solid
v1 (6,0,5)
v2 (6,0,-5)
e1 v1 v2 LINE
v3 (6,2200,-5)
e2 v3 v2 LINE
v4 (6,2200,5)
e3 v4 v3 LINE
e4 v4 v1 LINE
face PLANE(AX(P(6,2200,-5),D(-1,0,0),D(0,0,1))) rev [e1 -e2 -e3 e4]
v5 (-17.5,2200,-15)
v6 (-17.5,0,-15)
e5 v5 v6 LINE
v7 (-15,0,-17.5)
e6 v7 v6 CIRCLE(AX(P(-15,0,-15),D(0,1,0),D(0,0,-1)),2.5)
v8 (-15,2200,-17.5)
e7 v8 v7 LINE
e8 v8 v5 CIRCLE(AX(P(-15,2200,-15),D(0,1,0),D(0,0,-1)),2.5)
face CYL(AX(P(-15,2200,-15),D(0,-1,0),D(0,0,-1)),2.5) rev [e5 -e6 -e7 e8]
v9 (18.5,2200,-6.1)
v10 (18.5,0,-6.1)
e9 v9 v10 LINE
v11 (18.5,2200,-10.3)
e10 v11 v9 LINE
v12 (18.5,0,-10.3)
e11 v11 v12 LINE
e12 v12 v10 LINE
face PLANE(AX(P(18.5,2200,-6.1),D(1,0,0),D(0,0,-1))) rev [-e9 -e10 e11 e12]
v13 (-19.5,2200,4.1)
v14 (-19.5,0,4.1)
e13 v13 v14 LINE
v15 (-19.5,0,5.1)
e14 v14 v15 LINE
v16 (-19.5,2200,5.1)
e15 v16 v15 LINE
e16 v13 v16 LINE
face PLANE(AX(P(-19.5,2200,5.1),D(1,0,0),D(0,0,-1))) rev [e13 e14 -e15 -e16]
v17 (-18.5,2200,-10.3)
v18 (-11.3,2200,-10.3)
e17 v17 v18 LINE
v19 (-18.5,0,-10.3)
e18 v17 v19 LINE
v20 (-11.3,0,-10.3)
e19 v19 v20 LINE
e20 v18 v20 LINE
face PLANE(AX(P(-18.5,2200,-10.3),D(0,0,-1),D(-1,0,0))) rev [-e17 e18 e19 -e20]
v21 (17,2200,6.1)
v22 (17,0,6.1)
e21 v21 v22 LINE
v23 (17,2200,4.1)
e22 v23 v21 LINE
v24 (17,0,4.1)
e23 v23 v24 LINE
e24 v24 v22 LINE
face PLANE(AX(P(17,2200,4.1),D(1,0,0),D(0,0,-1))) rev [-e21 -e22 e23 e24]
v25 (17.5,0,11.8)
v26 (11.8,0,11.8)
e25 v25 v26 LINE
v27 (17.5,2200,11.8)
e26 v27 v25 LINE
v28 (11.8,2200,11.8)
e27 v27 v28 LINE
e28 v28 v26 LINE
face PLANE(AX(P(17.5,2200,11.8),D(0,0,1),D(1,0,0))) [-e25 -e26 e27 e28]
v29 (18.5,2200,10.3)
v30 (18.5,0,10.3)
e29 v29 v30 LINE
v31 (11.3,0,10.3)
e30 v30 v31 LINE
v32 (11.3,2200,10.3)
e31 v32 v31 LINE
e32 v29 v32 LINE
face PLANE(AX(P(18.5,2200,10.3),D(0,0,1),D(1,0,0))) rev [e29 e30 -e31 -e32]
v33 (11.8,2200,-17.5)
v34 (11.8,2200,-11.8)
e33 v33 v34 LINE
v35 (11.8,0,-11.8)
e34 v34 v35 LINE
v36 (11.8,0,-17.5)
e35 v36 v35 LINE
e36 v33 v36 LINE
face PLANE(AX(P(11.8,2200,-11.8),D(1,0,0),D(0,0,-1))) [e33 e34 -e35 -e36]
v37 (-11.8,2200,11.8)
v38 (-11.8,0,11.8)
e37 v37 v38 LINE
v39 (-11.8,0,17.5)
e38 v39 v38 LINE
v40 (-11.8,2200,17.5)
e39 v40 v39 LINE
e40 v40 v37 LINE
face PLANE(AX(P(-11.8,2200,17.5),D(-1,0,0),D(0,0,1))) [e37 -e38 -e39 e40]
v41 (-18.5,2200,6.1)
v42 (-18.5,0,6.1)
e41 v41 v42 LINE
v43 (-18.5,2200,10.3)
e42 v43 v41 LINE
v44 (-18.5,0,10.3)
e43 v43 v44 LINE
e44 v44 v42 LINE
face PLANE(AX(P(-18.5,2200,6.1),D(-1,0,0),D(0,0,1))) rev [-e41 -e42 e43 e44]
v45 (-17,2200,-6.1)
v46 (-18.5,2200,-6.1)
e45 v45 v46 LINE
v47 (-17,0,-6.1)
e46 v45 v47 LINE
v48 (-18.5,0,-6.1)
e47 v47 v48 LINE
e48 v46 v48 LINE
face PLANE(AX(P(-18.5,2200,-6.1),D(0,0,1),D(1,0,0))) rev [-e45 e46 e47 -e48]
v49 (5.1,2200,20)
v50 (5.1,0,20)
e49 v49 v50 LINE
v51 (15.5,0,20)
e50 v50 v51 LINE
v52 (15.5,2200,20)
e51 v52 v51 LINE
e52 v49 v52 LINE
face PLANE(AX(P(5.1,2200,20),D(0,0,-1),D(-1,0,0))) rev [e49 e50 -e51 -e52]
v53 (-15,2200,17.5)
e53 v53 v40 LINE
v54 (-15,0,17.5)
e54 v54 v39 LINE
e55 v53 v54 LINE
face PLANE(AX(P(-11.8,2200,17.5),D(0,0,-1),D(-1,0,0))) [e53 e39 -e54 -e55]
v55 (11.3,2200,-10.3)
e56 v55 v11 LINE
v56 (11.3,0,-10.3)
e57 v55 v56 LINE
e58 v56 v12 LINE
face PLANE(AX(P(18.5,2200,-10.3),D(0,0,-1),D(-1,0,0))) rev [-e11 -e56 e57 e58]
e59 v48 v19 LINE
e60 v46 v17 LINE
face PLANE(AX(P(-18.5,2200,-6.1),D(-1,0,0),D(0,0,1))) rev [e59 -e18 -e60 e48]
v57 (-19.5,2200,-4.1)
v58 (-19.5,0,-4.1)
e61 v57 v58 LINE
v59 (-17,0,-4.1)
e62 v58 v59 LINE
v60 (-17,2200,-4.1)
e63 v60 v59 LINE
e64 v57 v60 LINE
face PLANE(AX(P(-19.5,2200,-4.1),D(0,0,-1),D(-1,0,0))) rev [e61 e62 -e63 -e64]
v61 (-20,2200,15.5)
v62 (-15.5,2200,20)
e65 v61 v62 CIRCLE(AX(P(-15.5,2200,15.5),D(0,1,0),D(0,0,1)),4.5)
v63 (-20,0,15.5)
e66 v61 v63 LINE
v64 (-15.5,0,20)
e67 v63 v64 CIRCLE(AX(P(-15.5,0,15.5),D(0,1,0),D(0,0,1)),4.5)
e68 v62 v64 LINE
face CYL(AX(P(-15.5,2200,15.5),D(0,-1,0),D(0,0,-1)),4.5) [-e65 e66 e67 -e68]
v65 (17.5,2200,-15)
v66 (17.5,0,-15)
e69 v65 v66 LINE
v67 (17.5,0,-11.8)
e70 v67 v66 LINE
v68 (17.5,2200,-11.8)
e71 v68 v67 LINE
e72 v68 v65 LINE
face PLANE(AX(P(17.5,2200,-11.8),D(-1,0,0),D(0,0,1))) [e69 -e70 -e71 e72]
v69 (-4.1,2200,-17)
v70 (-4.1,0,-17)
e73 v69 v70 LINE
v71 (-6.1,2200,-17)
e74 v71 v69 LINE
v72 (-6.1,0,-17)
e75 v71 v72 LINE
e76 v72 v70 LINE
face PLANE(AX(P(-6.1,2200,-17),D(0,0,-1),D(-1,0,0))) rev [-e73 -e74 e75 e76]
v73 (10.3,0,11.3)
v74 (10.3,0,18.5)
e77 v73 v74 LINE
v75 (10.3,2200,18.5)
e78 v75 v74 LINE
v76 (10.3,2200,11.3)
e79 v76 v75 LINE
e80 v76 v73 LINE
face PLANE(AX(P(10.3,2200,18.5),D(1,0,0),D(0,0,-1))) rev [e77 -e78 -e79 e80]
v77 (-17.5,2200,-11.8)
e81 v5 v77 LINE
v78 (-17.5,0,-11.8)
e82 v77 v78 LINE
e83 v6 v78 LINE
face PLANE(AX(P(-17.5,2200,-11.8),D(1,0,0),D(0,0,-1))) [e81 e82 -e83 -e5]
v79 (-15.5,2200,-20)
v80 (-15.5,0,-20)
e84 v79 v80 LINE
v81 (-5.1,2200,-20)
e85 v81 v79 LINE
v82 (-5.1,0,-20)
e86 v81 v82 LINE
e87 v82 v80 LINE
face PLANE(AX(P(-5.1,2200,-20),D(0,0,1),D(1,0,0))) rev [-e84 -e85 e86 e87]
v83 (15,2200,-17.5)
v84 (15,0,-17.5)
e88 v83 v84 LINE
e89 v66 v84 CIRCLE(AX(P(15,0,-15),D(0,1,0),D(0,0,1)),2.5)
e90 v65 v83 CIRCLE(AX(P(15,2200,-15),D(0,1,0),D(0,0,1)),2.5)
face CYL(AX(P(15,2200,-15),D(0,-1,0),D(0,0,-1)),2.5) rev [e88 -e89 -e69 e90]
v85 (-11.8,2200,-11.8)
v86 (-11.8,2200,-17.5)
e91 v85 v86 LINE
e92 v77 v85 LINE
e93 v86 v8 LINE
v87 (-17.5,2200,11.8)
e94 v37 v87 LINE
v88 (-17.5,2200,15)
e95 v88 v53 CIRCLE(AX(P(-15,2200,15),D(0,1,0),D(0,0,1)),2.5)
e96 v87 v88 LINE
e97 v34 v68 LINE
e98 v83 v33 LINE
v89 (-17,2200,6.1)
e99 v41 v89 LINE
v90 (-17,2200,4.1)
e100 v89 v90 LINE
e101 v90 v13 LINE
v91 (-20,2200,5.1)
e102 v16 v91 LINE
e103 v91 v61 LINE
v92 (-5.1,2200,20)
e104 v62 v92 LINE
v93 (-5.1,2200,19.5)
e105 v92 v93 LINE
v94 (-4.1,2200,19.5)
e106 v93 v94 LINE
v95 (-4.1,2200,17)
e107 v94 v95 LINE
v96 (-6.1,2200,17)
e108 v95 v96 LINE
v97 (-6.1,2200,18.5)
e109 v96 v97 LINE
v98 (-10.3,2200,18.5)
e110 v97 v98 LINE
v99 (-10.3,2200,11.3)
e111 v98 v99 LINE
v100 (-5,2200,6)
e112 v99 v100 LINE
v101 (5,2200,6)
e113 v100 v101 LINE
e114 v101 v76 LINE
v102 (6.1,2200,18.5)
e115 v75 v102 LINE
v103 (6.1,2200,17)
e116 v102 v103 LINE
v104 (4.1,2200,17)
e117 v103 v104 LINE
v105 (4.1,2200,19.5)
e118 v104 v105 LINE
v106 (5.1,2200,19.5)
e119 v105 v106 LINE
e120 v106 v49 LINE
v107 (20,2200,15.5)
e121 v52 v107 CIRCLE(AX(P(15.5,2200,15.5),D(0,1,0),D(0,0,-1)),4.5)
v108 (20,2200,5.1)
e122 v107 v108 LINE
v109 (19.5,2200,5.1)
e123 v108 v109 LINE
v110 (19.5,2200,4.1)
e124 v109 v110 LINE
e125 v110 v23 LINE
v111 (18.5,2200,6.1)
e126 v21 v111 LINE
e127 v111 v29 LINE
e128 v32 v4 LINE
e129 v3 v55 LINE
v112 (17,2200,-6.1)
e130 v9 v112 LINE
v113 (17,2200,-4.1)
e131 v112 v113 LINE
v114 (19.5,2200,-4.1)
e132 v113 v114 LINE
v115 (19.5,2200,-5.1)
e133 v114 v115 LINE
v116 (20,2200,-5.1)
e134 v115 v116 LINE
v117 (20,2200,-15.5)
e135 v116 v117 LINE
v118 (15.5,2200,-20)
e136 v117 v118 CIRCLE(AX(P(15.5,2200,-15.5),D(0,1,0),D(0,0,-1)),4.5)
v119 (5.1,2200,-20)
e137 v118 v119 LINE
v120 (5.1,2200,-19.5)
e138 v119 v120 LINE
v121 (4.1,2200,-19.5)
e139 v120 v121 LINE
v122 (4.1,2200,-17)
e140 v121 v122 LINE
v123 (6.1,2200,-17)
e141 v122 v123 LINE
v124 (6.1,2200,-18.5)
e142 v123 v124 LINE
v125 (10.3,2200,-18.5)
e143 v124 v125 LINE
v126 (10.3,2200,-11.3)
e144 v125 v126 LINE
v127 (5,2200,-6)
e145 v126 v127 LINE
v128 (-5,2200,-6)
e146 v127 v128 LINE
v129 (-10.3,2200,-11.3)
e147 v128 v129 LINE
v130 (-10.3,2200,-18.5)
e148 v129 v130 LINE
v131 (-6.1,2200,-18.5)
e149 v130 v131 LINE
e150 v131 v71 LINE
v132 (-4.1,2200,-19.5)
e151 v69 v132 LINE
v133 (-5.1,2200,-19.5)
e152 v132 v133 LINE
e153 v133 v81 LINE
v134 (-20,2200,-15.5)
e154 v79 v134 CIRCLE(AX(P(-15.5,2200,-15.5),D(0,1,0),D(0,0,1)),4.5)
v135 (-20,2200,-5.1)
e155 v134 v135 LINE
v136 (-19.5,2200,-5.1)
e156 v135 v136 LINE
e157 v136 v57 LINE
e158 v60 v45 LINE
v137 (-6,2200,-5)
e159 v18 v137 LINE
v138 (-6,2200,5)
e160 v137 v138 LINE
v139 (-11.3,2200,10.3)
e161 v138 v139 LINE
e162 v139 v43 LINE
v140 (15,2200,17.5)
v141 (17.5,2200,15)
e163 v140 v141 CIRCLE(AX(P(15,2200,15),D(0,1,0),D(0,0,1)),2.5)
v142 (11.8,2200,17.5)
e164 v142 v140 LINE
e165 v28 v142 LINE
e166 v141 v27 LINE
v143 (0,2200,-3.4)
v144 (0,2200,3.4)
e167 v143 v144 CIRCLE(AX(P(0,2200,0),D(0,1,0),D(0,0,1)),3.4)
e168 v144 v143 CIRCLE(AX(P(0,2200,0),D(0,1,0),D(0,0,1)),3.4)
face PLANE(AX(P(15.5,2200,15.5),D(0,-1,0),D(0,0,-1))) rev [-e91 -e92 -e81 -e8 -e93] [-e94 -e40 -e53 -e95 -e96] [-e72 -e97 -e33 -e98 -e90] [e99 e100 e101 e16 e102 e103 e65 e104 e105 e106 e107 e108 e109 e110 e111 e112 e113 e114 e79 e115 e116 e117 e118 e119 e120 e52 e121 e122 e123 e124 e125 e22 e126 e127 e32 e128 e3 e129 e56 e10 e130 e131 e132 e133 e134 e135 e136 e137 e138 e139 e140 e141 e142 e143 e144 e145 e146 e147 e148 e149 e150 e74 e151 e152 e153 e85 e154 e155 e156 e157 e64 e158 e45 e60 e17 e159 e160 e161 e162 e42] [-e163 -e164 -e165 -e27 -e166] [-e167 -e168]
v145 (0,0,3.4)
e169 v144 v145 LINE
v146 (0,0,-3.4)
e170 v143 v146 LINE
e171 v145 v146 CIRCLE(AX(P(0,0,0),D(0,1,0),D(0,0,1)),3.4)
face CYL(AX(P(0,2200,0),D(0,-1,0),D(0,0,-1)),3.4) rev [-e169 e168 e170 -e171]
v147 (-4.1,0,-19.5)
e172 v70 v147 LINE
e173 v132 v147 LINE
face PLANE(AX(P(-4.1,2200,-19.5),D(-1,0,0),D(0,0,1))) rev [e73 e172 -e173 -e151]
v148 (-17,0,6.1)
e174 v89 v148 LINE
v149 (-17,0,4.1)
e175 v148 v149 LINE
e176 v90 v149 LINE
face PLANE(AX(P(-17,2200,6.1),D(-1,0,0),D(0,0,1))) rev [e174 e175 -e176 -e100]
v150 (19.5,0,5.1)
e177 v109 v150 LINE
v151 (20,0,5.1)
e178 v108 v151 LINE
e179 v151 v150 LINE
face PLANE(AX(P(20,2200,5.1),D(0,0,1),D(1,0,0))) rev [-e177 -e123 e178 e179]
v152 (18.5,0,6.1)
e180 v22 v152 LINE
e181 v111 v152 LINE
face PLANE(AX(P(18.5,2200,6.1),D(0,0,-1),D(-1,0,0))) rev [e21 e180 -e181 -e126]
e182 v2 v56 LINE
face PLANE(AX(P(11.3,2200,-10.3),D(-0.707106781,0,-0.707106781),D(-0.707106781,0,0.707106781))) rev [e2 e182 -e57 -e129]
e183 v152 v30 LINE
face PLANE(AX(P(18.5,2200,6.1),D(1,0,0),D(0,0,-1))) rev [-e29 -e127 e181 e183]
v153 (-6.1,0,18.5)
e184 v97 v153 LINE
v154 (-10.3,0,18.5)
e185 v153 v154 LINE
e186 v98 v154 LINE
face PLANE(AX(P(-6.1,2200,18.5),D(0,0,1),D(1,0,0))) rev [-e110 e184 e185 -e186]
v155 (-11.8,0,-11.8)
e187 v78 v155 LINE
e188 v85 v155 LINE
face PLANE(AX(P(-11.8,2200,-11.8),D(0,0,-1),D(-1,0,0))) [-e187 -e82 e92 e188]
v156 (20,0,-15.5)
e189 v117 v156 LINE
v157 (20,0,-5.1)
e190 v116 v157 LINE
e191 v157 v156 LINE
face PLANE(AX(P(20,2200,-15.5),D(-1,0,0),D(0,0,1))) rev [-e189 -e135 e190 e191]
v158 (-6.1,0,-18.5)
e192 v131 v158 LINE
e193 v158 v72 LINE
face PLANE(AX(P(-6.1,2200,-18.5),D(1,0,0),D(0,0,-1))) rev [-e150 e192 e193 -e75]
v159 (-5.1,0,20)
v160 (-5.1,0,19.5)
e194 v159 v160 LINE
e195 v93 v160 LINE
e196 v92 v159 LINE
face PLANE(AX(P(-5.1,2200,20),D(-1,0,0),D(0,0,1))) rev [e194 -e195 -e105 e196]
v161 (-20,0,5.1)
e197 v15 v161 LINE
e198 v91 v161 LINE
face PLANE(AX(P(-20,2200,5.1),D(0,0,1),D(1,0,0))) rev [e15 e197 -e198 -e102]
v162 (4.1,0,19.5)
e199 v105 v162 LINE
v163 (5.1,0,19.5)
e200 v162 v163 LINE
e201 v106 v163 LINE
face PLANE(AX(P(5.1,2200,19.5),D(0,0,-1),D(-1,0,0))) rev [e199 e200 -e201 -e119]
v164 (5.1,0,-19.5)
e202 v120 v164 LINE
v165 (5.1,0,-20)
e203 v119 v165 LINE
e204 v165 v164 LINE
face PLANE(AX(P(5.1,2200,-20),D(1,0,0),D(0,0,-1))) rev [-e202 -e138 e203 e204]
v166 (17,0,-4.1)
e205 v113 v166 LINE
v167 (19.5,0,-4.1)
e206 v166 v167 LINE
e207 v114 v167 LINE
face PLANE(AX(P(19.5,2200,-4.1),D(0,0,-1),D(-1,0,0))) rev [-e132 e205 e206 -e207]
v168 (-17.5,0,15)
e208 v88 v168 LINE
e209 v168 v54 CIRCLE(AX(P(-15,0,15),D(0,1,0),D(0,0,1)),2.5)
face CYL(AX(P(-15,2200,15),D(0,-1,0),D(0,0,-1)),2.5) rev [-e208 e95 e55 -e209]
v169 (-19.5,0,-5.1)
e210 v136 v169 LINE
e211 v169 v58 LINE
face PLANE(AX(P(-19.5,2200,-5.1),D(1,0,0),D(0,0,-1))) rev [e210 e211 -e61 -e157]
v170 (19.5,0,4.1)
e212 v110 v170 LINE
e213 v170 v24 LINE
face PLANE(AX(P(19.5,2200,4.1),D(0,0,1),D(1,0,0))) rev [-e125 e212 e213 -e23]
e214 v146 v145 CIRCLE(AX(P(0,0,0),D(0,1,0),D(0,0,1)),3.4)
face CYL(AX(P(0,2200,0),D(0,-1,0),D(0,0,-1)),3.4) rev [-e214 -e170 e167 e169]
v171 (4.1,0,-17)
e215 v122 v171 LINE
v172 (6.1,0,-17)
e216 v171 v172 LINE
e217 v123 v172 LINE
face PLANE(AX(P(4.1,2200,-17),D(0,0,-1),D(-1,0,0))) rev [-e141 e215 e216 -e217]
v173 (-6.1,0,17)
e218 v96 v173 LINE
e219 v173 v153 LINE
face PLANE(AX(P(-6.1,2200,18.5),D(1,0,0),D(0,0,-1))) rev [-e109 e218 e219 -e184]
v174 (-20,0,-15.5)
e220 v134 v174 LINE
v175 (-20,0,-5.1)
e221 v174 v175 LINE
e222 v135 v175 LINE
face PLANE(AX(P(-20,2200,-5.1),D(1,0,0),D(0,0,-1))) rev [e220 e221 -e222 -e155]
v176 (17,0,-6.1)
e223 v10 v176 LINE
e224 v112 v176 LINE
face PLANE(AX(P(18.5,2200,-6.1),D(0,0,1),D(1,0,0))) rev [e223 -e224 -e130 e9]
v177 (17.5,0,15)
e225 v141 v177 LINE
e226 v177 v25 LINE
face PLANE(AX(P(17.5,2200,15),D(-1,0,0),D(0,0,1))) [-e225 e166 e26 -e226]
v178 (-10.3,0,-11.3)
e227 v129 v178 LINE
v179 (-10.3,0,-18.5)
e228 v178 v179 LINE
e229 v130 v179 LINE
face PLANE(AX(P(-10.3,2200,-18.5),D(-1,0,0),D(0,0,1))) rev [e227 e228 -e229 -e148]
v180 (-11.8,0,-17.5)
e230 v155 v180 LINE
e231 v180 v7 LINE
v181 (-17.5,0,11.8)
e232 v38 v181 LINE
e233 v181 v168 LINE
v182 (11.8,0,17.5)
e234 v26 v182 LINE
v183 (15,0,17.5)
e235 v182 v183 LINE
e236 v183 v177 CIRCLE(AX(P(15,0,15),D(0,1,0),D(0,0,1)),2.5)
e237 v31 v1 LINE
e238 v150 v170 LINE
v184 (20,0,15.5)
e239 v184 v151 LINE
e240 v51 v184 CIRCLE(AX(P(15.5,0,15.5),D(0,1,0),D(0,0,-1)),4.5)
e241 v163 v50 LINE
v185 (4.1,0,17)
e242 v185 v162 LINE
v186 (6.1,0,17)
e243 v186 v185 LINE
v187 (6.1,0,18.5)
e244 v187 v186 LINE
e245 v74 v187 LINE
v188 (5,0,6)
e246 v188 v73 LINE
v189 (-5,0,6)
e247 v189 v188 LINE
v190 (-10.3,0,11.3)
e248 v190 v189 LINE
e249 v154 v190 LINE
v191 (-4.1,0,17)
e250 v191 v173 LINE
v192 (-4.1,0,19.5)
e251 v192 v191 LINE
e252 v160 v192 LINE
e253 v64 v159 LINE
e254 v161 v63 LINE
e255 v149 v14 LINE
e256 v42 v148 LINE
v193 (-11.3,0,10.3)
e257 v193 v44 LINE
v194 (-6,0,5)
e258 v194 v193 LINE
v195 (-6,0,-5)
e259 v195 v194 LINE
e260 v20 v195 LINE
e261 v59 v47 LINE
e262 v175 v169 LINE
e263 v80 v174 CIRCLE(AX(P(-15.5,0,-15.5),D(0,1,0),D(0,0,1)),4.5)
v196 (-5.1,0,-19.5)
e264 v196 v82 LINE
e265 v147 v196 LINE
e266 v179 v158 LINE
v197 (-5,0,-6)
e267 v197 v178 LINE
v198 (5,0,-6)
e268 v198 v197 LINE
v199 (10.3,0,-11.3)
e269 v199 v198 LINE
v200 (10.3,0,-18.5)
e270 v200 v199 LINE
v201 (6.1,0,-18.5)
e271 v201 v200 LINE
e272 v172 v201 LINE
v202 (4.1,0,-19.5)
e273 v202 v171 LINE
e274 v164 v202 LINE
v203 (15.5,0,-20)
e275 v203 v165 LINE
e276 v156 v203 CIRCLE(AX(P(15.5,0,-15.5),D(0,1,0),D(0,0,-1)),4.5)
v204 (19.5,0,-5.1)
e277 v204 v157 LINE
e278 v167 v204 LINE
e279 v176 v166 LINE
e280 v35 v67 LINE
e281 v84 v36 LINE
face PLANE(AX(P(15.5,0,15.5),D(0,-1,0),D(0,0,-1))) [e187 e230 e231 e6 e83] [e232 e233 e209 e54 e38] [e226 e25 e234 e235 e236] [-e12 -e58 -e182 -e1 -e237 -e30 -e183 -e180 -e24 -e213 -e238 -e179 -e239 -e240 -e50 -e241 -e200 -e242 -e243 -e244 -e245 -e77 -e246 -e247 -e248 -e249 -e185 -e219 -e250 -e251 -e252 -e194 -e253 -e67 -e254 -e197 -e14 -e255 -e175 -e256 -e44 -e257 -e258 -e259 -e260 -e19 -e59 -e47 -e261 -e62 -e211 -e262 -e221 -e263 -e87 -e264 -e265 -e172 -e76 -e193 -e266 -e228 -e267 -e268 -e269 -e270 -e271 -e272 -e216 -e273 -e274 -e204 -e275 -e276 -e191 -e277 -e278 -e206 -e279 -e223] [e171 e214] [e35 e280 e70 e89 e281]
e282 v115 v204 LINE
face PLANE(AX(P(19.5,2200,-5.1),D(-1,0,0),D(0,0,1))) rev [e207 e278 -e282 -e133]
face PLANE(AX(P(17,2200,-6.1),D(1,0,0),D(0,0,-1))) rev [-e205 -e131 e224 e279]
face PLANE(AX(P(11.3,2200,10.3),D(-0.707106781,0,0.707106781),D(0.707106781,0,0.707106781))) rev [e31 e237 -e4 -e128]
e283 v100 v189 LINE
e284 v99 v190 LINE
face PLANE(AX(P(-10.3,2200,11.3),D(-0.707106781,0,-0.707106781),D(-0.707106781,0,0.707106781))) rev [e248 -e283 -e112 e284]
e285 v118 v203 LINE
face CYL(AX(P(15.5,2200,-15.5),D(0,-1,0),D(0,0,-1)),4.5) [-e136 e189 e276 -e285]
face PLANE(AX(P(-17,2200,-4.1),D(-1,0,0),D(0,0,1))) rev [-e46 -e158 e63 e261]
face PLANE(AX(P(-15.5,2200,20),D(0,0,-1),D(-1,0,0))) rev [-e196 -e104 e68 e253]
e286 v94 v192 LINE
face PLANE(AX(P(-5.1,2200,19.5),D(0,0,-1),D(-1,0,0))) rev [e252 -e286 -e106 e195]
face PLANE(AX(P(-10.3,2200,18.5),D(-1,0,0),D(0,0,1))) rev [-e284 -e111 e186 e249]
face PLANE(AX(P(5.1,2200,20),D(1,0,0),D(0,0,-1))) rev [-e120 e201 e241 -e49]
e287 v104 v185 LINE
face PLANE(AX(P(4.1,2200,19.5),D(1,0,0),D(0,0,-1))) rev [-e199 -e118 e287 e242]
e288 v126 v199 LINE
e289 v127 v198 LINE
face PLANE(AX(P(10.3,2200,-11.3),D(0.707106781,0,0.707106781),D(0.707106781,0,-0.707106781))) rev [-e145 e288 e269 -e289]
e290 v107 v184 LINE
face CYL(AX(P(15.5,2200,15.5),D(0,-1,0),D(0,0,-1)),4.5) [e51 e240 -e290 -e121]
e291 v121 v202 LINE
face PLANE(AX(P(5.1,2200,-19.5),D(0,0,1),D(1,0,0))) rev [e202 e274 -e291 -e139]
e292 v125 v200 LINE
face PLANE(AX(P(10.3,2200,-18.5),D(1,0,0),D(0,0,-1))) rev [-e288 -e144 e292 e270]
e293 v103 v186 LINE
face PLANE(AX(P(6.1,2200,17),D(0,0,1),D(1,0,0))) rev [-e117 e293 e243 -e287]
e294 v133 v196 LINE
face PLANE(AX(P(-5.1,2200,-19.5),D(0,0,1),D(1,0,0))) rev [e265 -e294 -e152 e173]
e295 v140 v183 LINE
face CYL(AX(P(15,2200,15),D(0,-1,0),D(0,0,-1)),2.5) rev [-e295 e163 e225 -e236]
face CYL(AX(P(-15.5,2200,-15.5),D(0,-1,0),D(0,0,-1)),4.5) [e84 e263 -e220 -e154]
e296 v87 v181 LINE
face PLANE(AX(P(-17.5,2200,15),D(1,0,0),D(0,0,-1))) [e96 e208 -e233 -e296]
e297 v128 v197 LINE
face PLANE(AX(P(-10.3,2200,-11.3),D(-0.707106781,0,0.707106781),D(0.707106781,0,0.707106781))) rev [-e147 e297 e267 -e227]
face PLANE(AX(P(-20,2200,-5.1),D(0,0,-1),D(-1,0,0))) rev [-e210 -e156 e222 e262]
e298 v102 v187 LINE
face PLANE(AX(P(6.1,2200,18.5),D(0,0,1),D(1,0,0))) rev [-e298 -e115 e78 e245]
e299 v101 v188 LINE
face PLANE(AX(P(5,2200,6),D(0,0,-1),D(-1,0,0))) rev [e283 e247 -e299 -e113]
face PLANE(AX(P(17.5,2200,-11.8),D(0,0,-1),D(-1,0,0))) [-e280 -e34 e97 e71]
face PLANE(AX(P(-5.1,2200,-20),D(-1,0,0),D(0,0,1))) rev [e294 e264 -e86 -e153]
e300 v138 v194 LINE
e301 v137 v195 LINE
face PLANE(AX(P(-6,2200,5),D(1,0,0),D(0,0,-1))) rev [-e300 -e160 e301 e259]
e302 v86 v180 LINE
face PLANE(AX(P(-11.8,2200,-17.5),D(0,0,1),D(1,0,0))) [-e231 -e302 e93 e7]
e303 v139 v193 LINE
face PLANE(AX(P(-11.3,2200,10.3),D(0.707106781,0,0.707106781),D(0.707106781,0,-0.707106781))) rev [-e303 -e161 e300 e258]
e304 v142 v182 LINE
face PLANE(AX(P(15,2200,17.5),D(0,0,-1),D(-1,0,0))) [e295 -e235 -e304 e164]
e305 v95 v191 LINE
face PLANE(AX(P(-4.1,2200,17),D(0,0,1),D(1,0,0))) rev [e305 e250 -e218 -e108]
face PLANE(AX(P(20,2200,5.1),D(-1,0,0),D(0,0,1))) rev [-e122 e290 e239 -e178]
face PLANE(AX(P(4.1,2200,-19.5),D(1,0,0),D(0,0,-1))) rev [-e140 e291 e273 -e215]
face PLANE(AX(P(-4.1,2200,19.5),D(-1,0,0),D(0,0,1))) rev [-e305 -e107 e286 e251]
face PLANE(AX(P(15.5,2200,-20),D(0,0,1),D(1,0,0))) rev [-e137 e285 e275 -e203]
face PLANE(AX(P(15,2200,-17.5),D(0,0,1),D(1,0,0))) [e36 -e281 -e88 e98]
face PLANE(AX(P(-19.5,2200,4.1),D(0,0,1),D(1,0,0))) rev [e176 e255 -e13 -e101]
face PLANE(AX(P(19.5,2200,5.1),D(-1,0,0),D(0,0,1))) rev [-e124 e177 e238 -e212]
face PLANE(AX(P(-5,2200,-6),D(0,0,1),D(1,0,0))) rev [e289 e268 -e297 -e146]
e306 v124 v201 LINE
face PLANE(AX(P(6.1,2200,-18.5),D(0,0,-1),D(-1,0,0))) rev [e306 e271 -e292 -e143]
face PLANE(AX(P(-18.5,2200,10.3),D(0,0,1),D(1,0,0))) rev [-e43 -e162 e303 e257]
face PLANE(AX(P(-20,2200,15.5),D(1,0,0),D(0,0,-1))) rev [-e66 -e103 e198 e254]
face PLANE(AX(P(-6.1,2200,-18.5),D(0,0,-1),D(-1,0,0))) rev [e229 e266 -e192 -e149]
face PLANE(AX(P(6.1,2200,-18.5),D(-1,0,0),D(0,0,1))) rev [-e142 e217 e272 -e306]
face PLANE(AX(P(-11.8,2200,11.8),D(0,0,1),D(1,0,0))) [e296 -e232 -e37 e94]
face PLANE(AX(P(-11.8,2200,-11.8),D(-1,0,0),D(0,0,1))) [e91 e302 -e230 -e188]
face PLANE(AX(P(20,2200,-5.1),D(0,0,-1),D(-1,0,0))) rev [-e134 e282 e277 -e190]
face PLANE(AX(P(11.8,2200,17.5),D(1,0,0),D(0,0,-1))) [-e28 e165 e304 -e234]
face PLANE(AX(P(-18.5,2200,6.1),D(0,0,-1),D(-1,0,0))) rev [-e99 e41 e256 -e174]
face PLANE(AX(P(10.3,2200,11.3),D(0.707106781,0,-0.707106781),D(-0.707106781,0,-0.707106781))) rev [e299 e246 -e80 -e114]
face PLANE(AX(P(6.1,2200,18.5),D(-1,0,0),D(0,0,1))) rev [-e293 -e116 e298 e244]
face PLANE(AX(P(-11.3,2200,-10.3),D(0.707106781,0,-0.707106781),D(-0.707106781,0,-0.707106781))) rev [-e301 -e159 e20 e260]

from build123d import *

# Parameters (mm, degrees)
SKETCH1_R                 = 3.4
F_40_X_40L_X_R4_5_1_DEPTH = 2200


with BuildPart() as part:
    # Sketch1 → 铝型材 40 X 40L X R4.5(1) (new body)
    with BuildSketch(Plane(origin=(0, 0, 0), x_dir=(-1, 0, 0), z_dir=(0, 1, 0))):
        with BuildLine():
            Line((-5.1, 20), (-5.1, 19.5))
            Line((-5.1, 19.5), (-4.1, 19.5))
            Line((-4.1, 19.5), (-4.1, 17))
            Line((-4.1, 17), (-6.1, 17))
            Line((-6.1, 17), (-6.1, 18.5))
            Line((-6.1, 18.5), (-10.3, 18.5))
            Line((-10.3, 18.5), (-10.3, 11.3))
            Line((-10.3, 11.3), (-5, 6))
            Line((-5, 6), (5, 6))
            Line((5, 6), (10.3, 11.3))
            Line((10.3, 11.3), (10.3, 18.5))
            Line((10.3, 18.5), (6.1, 18.5))
            Line((6.1, 18.5), (6.1, 17))
            Line((6.1, 17), (4.1, 17))
            Line((4.1, 17), (4.1, 19.5))
            Line((4.1, 19.5), (5.1, 19.5))
            Line((5.1, 19.5), (5.1, 20))
            Line((5.1, 20), (15.5, 20))
            ThreePointArc((15.5, 20), (18.681980515, 18.681980515), (20, 15.5))
            Line((20, 15.5), (20, 5.1))
            Line((20, 5.1), (19.5, 5.1))
            Line((19.5, 5.1), (19.5, 4.1))
            Line((19.5, 4.1), (17, 4.1))
            Line((17, 4.1), (17, 6.1))
            Line((17, 6.1), (18.5, 6.1))
            Line((18.5, 6.1), (18.5, 10.3))
            Line((18.5, 10.3), (11.3, 10.3))
            Line((11.3, 10.3), (6, 5))
            Line((6, 5), (6, -5))
            Line((6, -5), (11.3, -10.3))
            Line((11.3, -10.3), (18.5, -10.3))
            Line((18.5, -10.3), (18.5, -6.1))
            Line((18.5, -6.1), (17, -6.1))
            Line((17, -6.1), (17, -4.1))
            Line((17, -4.1), (19.5, -4.1))
            Line((19.5, -4.1), (19.5, -5.1))
            Line((19.5, -5.1), (20, -5.1))
            Line((20, -5.1), (20, -15.5))
            ThreePointArc((20, -15.5), (18.681980515, -18.681980515), (15.5, -20))
            Line((15.5, -20), (5.1, -20))
            Line((5.1, -20), (5.1, -19.5))
            Line((5.1, -19.5), (4.1, -19.5))
            Line((4.1, -19.5), (4.1, -17))
            Line((4.1, -17), (6.1, -17))
            Line((6.1, -17), (6.1, -18.5))
            Line((6.1, -18.5), (10.3, -18.5))
            Line((10.3, -18.5), (10.3, -11.3))
            Line((10.3, -11.3), (5, -6))
            Line((5, -6), (-5, -6))
            Line((-5, -6), (-10.3, -11.3))
            Line((-10.3, -11.3), (-10.3, -18.5))
            Line((-10.3, -18.5), (-6.1, -18.5))
            Line((-6.1, -18.5), (-6.1, -17))
            Line((-6.1, -17), (-4.1, -17))
            Line((-4.1, -17), (-4.1, -19.5))
            Line((-4.1, -19.5), (-5.1, -19.5))
            Line((-5.1, -19.5), (-5.1, -20))
            Line((-5.1, -20), (-15.5, -20))
            ThreePointArc((-15.5, -20), (-18.681980515, -18.681980515), (-20, -15.5))
            Line((-20, -15.5), (-20, -5.1))
            Line((-20, -5.1), (-19.5, -5.1))
            Line((-19.5, -5.1), (-19.5, -4.1))
            Line((-19.5, -4.1), (-17, -4.1))
            Line((-17, -4.1), (-17, -6.1))
            Line((-17, -6.1), (-18.5, -6.1))
            Line((-18.5, -6.1), (-18.5, -10.3))
            Line((-18.5, -10.3), (-11.3, -10.3))
            Line((-11.3, -10.3), (-6, -5))
            Line((-6, -5), (-6, 5))
            Line((-6, 5), (-11.3, 10.3))
            Line((-11.3, 10.3), (-18.5, 10.3))
            Line((-18.5, 10.3), (-18.5, 6.1))
            Line((-18.5, 6.1), (-17, 6.1))
            Line((-17, 6.1), (-17, 4.1))
            Line((-17, 4.1), (-19.5, 4.1))
            Line((-19.5, 4.1), (-19.5, 5.1))
            Line((-19.5, 5.1), (-20, 5.1))
            Line((-20, 5.1), (-20, 15.5))
            ThreePointArc((-20, 15.5), (-18.681980515, 18.681980515), (-15.5, 20))
            Line((-15.5, 20), (-5.1, 20))
        make_face()
        Circle(SKETCH1_R, mode=Mode.SUBTRACT)
        with BuildLine():
            Line((11.8, 17.5), (15, 17.5))
            ThreePointArc((15, 17.5), (16.767766953, 16.767766953), (17.5, 15))
            Line((17.5, 15), (17.5, 11.8))
            Line((17.5, 11.8), (11.8, 11.8))
            Line((11.8, 11.8), (11.8, 17.5))
        make_face(mode=Mode.SUBTRACT)
        with BuildLine():
            Line((-15, 17.5), (-11.8, 17.5))
            Line((-11.8, 17.5), (-11.8, 11.8))
            Line((-11.8, 11.8), (-17.5, 11.8))
            Line((-17.5, 11.8), (-17.5, 15))
            ThreePointArc((-17.5, 15), (-16.767766953, 16.767766953), (-15, 17.5))
        make_face(mode=Mode.SUBTRACT)
        with BuildLine():
            Line((-17.5, -11.8), (-11.8, -11.8))
            Line((-11.8, -11.8), (-11.8, -17.5))
            Line((-11.8, -17.5), (-15, -17.5))
            ThreePointArc((-15, -17.5), (-16.767766953, -16.767766953), (-17.5, -15))
            Line((-17.5, -15), (-17.5, -11.8))
        make_face(mode=Mode.SUBTRACT)
        with BuildLine():
            Line((11.8, -11.8), (17.5, -11.8))
            Line((17.5, -11.8), (17.5, -15))
            ThreePointArc((17.5, -15), (16.767766953, -16.767766953), (15, -17.5))
            Line((15, -17.5), (11.8, -17.5))
            Line((11.8, -17.5), (11.8, -11.8))
        make_face(mode=Mode.SUBTRACT)
    extrude(amount=F_40_X_40L_X_R4_5_1_DEPTH)


solid = part.part
